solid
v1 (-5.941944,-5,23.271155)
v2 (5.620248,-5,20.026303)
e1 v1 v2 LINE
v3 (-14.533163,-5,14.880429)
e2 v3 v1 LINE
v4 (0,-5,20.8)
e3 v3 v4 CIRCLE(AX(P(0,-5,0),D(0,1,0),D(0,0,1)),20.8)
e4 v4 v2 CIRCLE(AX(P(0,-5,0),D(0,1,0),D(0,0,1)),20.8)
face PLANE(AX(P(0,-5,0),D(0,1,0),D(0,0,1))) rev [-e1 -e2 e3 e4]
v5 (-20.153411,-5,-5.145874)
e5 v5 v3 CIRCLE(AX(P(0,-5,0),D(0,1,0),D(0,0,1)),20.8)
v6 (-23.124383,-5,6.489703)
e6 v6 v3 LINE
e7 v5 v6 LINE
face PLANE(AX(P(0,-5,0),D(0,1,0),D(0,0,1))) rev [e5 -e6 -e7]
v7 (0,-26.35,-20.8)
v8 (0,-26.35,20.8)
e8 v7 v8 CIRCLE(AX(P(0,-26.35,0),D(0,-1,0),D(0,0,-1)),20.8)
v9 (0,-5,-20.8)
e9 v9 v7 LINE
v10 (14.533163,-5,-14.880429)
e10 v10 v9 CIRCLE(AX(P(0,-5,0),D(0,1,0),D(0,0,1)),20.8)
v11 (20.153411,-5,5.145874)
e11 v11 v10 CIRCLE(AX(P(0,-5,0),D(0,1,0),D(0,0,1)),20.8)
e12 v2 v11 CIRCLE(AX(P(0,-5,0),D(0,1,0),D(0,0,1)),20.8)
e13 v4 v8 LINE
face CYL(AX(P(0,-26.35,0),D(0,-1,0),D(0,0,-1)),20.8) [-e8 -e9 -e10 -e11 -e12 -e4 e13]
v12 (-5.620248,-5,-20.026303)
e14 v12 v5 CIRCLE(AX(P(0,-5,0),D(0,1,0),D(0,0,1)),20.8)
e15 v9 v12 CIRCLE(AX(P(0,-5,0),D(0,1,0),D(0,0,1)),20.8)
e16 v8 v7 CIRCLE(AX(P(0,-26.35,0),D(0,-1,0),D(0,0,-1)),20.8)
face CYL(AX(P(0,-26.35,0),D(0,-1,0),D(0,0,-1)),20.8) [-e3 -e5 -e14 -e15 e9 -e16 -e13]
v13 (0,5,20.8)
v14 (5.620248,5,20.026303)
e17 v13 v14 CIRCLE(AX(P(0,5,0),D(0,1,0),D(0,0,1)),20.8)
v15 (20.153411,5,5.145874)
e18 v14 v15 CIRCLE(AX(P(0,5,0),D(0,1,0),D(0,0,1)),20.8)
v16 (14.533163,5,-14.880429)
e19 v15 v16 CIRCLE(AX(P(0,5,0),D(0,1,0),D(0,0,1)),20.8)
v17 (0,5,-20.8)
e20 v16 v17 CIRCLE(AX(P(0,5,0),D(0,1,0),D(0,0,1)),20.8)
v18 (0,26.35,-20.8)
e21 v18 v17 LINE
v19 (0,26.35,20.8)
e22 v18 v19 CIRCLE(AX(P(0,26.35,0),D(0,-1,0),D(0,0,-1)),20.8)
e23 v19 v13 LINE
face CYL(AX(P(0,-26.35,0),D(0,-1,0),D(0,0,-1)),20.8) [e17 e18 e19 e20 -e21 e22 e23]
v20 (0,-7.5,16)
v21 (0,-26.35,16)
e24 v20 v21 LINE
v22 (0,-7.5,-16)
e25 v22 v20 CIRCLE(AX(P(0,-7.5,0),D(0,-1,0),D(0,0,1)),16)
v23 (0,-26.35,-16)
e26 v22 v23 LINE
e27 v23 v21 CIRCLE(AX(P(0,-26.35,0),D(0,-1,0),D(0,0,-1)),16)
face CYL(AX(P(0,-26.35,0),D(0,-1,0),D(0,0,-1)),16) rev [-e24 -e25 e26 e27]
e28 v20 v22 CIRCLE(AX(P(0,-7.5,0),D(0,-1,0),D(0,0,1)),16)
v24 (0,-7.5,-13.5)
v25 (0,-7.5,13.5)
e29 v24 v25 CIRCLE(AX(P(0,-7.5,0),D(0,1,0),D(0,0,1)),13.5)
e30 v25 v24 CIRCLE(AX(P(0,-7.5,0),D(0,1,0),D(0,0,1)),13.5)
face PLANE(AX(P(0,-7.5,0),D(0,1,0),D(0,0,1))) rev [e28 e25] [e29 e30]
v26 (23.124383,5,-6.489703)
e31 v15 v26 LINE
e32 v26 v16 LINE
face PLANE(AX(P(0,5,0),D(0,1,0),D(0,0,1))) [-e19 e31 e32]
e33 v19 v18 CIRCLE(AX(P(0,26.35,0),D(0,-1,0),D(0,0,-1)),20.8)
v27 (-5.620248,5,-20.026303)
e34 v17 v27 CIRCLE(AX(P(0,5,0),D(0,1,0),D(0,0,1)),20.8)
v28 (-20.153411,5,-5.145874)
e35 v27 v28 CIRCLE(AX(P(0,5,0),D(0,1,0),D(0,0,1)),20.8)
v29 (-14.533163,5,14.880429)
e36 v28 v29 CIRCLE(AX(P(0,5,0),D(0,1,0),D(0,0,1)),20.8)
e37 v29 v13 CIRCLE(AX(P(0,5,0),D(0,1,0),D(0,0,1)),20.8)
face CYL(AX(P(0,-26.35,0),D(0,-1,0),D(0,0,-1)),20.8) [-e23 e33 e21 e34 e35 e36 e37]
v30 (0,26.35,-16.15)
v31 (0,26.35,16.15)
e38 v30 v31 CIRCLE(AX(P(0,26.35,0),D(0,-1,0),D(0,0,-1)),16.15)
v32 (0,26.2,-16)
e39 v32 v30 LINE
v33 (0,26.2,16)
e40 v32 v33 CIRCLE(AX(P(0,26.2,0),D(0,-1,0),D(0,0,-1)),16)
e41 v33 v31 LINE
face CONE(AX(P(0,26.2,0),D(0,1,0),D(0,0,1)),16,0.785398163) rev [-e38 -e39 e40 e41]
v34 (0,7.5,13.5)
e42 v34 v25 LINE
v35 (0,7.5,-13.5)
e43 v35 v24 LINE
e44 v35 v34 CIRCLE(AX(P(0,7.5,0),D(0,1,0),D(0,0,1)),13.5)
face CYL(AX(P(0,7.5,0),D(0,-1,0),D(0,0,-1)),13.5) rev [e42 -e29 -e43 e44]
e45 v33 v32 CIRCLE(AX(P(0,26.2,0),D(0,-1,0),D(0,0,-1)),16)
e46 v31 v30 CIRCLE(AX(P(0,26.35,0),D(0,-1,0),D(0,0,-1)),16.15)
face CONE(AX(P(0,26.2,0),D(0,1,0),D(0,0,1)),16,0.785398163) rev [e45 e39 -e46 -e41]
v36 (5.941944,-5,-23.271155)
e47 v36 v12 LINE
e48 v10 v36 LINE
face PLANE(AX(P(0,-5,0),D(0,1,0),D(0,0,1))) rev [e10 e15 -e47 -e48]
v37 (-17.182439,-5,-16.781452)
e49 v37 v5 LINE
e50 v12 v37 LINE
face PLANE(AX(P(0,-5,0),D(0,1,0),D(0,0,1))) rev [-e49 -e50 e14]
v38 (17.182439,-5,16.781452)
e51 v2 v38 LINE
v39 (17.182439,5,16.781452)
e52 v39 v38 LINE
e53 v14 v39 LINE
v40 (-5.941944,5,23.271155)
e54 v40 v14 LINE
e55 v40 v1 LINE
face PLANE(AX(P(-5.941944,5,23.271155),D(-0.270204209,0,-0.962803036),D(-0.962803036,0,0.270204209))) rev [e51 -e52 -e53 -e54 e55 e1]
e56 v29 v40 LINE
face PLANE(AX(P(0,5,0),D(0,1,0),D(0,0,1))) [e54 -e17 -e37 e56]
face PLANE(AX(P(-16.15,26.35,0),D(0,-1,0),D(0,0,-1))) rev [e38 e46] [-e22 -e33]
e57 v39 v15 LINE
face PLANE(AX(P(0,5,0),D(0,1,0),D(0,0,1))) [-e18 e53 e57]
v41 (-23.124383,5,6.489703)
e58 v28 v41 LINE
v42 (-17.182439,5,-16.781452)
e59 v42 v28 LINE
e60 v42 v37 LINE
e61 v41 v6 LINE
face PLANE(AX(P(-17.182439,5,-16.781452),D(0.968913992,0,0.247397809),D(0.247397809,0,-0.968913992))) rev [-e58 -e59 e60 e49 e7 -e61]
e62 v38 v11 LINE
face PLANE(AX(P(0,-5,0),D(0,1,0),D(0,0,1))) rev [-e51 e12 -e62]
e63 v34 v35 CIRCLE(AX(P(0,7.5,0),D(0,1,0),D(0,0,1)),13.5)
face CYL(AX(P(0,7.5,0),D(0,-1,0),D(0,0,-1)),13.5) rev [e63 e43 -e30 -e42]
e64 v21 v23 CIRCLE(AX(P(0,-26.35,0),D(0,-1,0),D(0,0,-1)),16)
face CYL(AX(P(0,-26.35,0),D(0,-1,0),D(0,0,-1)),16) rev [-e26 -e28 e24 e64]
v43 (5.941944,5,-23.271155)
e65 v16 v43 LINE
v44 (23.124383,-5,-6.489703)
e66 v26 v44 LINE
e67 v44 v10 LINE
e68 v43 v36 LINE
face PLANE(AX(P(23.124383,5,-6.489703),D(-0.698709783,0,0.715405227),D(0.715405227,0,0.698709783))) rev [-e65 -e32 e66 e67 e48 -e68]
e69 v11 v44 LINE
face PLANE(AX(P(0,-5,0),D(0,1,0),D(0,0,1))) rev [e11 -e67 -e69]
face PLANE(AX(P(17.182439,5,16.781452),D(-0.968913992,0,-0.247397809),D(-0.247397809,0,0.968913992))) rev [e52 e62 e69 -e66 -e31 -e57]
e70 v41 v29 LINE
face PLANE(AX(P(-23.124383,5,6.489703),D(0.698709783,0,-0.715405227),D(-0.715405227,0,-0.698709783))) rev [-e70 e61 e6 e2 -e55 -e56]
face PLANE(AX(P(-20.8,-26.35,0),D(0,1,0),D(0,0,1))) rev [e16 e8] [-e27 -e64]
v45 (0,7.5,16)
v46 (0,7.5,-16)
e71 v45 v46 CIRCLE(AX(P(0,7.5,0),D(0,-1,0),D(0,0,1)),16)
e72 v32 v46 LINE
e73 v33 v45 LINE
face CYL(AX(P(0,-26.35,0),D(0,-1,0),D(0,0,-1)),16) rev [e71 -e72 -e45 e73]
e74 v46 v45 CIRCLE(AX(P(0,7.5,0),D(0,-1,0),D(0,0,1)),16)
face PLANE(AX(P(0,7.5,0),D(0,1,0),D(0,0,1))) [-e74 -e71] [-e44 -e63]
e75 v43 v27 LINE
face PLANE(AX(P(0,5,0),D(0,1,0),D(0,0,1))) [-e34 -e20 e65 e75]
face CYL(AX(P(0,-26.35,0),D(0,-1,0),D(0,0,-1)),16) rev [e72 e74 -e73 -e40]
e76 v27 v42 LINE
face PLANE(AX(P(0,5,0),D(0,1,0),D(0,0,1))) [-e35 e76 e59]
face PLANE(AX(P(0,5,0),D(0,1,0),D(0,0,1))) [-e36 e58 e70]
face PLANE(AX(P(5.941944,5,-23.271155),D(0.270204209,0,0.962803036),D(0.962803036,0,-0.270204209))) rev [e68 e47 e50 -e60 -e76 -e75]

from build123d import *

# Parameters (mm, degrees)
SKETCH_3_W          = 2.4
SKETCH_3_H          = 3.7
EXTRUDE_1_DEPTH     = 5
CUT_EXTRUDE_START   = -10
SKETCH_5_R          = 16
CUT_EXTRUDE_1_DEPTH = 10
SKETCH_6_R          = 17.5
SKETCH_6_R_2        = 13.5
EXTRUDE_2_DEPTH     = 7.5


with BuildPart() as part:
    # 草图2 → Revolve 1 (revolve)
    with BuildSketch(Plane.XY, mode=Mode.PRIVATE) as revolve_1_sk:
        Polygon((-16, 26.2), (-16, -26.35), (-20.8, -26.35), (-20.8, 26.35), (-16.15, 26.35), align=None)
    revolve(revolve_1_sk.sketch.rotate(Axis((0, -26.35, 0), (0, 1, 0)), 270), axis=Axis((0, -26.35, 0), (0, 1, 0)))

    # 草图3 → Revolve 1 2 (revolve)
    with BuildSketch(Plane.XY, mode=Mode.PRIVATE) as revolve_1_2_sk:
        with Locations((-14.8, 1.85)):
            Rectangle(SKETCH_3_W, SKETCH_3_H)
    revolve(revolve_1_2_sk.sketch.rotate(Axis((0, -26.35, 0), (0, 1, 0)), 270), axis=Axis((0, -26.35, 0), (0, 1, 0)))

    # 草图4 → 凸台-拉伸1 (add, symmetric)
    with BuildSketch(Plane(origin=(0, 0, 0), x_dir=(1, 0, 0), z_dir=(0, 1, 0))):
        Polygon((23.124383018, 6.489702871), (5.94194396, 23.271154576), (-17.182439058, 16.781451705), (-23.124383018, -6.489702871), (-5.94194396, -23.271154576), (17.182439058, -16.781451705), align=None)
    extrude(amount=EXTRUDE_1_DEPTH, both=True)

    # 草图5 → 切除-拉伸1 (cut)
    with BuildSketch(Plane(origin=(0, 5, 0), x_dir=(1, 0, 0), z_dir=(0, 1, 0)).offset(CUT_EXTRUDE_START)):
        with Locations(Location((0, 0, 0), (0, 0, 90))):
            Circle(SKETCH_5_R)
    extrude(amount=CUT_EXTRUDE_1_DEPTH, mode=Mode.SUBTRACT)

    # 草图6 → 凸台-拉伸2 (add, symmetric)
    with BuildSketch(Plane(origin=(0, 0, 0), x_dir=(1, 0, 0), z_dir=(0, 1, 0))):
        Circle(SKETCH_6_R)
        with Locations(Location((0, 0, 0), (0, 0, 270))):
            Circle(SKETCH_6_R_2, mode=Mode.SUBTRACT)
    extrude(amount=EXTRUDE_2_DEPTH, both=True)


solid = part.part
